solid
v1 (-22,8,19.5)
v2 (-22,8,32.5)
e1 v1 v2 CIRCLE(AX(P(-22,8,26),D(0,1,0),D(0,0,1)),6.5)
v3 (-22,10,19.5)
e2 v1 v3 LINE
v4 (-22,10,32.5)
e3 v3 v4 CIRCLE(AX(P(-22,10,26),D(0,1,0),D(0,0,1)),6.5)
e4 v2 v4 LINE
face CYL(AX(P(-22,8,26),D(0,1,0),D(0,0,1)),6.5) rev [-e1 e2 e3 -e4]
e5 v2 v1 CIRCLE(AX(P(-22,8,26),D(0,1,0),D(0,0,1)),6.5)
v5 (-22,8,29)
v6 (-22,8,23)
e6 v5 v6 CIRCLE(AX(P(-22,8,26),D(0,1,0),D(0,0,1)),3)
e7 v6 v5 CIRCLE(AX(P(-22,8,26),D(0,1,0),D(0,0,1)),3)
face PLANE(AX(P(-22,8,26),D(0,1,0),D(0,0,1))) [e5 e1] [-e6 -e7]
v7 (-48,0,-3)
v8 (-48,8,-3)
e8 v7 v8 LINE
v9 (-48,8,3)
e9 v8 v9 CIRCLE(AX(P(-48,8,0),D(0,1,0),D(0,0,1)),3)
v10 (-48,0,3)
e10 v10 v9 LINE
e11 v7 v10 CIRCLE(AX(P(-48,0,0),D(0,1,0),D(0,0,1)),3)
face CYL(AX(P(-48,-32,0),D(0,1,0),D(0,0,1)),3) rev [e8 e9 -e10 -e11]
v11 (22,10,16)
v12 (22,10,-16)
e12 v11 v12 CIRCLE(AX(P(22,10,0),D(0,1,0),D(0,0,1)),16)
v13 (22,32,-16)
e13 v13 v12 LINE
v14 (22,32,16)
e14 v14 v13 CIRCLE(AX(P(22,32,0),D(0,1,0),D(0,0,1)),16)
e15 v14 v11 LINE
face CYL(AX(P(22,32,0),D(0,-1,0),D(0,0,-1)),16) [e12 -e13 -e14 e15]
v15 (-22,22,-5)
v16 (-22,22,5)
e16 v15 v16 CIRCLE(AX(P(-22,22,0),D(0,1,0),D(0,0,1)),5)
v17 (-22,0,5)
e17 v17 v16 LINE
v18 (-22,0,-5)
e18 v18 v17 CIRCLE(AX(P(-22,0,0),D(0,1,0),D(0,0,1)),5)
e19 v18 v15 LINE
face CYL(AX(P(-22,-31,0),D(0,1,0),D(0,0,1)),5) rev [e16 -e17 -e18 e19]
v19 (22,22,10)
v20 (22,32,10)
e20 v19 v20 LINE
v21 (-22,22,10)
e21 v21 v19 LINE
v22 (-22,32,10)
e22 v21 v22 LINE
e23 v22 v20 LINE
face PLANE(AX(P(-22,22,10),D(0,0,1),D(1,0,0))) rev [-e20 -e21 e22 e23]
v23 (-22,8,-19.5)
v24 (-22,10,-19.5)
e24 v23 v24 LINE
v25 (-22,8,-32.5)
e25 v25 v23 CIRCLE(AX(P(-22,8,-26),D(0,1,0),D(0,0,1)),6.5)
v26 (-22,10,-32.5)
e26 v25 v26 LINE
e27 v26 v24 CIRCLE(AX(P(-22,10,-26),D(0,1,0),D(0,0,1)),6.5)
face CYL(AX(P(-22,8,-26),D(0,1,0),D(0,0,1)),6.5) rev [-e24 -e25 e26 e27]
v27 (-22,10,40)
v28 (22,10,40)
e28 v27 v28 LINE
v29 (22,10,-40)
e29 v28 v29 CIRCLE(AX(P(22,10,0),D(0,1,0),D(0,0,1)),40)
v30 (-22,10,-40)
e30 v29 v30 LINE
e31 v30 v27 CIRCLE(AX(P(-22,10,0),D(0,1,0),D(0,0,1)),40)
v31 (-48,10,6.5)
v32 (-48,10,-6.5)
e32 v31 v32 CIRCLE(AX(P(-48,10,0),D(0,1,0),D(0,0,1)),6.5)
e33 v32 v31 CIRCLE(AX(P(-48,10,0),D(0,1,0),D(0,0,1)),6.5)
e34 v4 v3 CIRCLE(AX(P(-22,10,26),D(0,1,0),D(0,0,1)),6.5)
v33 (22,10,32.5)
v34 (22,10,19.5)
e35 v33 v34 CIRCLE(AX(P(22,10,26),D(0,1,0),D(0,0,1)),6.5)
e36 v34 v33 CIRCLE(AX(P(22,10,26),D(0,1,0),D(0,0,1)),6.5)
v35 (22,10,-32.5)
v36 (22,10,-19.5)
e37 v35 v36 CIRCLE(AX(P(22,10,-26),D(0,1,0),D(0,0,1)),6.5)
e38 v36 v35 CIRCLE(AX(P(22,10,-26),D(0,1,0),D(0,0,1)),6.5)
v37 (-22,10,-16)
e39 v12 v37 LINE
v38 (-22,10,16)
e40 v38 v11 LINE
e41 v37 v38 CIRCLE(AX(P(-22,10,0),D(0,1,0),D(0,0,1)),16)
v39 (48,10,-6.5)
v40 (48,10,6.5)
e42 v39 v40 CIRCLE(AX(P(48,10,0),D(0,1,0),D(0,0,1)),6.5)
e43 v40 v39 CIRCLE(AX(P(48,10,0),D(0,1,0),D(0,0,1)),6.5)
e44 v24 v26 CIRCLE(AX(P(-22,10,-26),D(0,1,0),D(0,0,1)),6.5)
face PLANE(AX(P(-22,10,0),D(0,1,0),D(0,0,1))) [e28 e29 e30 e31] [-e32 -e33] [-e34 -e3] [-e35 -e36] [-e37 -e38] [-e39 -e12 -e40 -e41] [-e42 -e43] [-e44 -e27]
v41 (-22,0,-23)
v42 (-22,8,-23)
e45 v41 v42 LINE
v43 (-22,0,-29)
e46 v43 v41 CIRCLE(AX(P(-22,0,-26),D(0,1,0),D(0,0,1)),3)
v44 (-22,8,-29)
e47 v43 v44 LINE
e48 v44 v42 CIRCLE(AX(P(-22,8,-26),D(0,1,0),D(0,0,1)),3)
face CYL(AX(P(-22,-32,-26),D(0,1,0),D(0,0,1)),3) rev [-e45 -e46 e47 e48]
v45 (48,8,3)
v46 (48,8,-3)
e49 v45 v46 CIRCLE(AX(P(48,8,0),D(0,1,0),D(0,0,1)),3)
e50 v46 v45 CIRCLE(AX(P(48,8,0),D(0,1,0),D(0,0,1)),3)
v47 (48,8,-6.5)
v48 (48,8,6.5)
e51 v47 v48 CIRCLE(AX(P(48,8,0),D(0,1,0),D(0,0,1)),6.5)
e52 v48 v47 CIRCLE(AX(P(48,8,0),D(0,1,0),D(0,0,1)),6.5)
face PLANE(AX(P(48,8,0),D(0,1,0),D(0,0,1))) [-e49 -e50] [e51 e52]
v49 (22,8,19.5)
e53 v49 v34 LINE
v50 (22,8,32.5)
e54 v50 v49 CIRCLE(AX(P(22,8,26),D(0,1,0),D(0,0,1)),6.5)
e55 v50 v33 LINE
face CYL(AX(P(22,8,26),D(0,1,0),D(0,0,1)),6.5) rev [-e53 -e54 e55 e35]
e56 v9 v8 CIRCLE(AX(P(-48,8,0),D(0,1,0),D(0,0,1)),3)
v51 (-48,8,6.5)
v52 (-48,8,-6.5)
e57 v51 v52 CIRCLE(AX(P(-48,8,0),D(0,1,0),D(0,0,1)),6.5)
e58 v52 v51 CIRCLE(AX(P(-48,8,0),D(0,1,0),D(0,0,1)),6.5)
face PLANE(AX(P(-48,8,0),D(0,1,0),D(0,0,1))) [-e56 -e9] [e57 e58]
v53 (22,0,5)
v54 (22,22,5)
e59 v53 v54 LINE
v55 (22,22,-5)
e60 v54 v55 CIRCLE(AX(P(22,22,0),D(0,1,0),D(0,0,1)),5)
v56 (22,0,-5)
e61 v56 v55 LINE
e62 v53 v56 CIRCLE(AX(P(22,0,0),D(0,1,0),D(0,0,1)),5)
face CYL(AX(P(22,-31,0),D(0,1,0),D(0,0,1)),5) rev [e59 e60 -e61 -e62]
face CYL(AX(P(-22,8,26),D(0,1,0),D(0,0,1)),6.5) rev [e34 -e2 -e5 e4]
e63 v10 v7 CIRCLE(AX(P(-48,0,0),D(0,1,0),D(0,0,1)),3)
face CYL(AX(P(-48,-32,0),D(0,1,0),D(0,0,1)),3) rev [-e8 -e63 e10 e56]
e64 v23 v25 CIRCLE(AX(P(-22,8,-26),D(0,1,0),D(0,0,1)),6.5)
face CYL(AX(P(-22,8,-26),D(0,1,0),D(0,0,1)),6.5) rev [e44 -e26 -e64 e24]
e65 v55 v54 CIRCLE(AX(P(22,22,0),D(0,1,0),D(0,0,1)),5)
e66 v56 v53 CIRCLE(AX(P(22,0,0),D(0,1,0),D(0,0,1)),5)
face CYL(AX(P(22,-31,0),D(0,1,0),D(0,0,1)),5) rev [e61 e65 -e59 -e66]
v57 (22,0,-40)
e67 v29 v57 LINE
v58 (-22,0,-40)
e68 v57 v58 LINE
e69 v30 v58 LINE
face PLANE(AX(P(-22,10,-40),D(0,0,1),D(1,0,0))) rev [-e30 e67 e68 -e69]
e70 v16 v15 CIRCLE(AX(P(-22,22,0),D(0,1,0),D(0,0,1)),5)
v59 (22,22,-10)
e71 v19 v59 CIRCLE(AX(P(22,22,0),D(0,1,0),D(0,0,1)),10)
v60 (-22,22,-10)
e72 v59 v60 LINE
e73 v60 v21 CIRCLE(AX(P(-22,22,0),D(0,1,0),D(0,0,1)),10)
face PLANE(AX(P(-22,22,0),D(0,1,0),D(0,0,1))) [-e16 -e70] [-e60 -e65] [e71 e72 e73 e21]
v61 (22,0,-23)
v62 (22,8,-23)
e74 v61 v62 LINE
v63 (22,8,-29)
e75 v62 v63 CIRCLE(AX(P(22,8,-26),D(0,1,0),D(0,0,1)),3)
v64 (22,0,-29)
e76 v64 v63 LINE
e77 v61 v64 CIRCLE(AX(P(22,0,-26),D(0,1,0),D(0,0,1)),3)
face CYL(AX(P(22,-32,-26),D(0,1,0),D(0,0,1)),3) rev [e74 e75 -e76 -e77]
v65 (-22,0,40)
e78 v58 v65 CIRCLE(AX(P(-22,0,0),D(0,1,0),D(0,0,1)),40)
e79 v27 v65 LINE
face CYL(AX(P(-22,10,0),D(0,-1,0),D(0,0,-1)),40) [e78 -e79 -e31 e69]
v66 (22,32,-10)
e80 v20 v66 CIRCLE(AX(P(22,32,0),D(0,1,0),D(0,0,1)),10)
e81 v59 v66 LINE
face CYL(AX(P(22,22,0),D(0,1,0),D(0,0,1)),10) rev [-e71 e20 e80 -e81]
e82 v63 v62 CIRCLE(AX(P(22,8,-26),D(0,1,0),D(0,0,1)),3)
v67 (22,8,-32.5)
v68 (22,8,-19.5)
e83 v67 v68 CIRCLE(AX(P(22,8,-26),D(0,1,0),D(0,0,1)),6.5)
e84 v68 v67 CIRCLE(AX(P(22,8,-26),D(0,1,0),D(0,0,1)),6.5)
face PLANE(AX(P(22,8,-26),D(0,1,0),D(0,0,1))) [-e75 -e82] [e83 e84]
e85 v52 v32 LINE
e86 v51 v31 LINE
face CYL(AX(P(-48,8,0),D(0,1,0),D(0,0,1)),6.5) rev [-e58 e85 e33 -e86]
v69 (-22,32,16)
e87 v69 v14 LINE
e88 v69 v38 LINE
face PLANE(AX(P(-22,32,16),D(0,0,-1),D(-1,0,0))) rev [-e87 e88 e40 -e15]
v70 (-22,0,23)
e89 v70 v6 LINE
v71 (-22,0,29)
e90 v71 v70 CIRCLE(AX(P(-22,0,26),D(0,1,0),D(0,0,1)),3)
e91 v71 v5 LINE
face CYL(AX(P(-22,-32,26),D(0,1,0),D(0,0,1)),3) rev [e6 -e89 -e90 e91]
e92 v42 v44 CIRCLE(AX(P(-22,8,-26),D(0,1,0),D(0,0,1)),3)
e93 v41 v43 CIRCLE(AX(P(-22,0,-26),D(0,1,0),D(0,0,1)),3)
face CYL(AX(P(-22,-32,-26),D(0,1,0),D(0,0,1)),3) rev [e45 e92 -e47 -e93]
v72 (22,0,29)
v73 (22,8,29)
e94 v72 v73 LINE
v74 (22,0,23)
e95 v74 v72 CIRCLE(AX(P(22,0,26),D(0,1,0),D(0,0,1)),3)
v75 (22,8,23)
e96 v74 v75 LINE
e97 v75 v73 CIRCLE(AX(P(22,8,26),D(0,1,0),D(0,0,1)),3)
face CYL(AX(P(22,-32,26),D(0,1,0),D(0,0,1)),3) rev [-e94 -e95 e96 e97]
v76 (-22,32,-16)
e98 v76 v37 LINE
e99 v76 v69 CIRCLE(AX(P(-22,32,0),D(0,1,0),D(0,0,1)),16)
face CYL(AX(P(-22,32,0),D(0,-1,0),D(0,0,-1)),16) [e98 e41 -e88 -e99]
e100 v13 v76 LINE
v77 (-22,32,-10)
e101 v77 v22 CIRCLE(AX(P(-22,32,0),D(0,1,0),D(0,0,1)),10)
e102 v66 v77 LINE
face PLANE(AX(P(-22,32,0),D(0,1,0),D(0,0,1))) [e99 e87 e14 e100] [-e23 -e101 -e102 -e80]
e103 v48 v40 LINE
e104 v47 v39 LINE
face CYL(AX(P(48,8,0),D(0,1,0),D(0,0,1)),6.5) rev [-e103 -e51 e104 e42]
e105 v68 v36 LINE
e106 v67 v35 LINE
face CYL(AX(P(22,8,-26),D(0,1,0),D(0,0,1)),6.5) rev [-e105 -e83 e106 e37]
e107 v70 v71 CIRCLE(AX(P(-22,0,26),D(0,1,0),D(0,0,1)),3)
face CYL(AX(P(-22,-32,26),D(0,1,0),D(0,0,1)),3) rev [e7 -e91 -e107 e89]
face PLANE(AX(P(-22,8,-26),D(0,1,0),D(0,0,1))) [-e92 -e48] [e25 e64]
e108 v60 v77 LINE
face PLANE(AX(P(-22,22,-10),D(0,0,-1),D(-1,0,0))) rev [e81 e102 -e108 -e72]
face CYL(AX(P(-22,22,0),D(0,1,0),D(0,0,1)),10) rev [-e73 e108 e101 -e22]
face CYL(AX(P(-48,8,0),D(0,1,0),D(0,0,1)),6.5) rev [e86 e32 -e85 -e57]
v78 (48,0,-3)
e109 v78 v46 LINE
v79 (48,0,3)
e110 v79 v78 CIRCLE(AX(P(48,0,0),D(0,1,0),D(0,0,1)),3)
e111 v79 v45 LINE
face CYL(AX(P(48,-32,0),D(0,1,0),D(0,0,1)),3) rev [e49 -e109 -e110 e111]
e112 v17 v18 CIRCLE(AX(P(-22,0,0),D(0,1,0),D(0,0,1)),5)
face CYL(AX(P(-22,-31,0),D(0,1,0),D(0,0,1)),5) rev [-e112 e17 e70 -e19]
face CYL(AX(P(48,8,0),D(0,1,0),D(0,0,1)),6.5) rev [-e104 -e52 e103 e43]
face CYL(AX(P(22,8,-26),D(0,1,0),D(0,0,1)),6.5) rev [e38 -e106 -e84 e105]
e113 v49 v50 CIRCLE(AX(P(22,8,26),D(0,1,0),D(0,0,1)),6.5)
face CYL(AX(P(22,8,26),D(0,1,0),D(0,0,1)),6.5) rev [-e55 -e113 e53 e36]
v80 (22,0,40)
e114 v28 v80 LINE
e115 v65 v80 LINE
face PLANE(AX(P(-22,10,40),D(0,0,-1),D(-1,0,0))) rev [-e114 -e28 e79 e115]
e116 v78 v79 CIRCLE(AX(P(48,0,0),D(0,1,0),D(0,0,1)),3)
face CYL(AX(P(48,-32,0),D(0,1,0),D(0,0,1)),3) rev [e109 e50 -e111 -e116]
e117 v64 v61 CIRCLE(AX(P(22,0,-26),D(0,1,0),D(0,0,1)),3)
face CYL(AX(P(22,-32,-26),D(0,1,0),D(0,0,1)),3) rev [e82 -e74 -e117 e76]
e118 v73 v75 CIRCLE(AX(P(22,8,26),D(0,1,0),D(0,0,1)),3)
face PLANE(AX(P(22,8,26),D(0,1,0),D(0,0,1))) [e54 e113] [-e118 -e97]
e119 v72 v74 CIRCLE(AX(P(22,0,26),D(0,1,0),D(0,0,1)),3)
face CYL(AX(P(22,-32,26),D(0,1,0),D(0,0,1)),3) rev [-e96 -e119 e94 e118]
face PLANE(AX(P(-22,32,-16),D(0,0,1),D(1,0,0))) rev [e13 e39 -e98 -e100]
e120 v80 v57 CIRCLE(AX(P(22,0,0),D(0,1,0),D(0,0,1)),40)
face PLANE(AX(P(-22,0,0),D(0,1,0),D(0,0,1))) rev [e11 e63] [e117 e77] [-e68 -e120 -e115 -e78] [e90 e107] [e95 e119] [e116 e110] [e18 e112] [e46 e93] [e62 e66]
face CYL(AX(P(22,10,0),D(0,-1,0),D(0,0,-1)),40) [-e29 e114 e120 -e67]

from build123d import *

# Parameters (mm, degrees)
BASE_FLANGE_DEPTH             = 10
SLOT_BOSS_DEPTH               = 22
SLOT_POCKET_DEPTH             = 10
SLOT_THROUGH_CUT_SKETCH_R     = 5
SLOT_THROUGH_CUT_DEPTH        = 53
COUNTERBORES_SKETCH_R         = 6.5
COUNTERBORES_6X_DEPTH_2_DEPTH = 2
MOUNTING_HOLES_SKETCH_R       = 3
MOUNTING_HOLES_6X_DEPTH       = 40


with BuildPart() as part:
    # Base Flange Sketch → Base Flange (new body)
    with BuildSketch(Plane(origin=(0, 0, 0), x_dir=(1, 0, 0), z_dir=(0, 1, 0))):
        with BuildLine():
            Line((-22, -40), (22, -40))
            ThreePointArc((22, -40), (62, 0), (22, 40))
            Line((22, 40), (-22, 40))
            ThreePointArc((-22, 40), (-62, 0), (-22, -40))
        make_face()
    extrude(amount=BASE_FLANGE_DEPTH)

    # Slot Boss Sketch → Slot Boss (add)
    with BuildSketch(Plane(origin=(0, 10, 0), x_dir=(1, 0, 0), z_dir=(0, 1, 0))):
        with BuildLine():
            Line((-22, 16), (22, 16))
            ThreePointArc((22, 16), (38, 0), (22, -16))
            Line((22, -16), (-22, -16))
            ThreePointArc((-22, -16), (-38, 0), (-22, 16))
        make_face()
    extrude(amount=SLOT_BOSS_DEPTH)

    # Slot Pocket Sketch → Slot Pocket (cut)
    with BuildSketch(Plane(origin=(0, 32, 0), x_dir=(1, 0, 0), z_dir=(0, 1, 0))):
        with BuildLine():
            Line((-22, 10), (22, 10))
            ThreePointArc((22, 10), (32, 0), (22, -10))
            Line((22, -10), (-22, -10))
            ThreePointArc((-22, -10), (-32, 0), (-22, 10))
        make_face()
    extrude(amount=-SLOT_POCKET_DEPTH, mode=Mode.SUBTRACT)

    # Slot Through Cut Sketch → Slot Through Cut (cut)
    with BuildSketch(Plane(origin=(0, 22, 0), x_dir=(1, 0, 0), z_dir=(0, 1, 0))):
        with Locations(Location((22, 0, 0), (0, 0, 270))):
            Circle(SLOT_THROUGH_CUT_SKETCH_R)
        with Locations(Location((-22, 0, 0), (0, 0, 270))):
            Circle(SLOT_THROUGH_CUT_SKETCH_R)
    extrude(amount=-SLOT_THROUGH_CUT_DEPTH, mode=Mode.SUBTRACT)

    # Counterbores Sketch → Counterbores 6x Depth 2 (cut)
    with BuildSketch(Plane(origin=(0, 10, 0), x_dir=(1, 0, 0), z_dir=(0, 1, 0))):
        with Locations(Location((48, 0, 0), (0, 0, 270))):
            Circle(COUNTERBORES_SKETCH_R)
        with Locations(Location((22, 26, 0), (0, 0, 270))):
            Circle(COUNTERBORES_SKETCH_R)
        with Locations(Location((-22, 26, 0), (0, 0, 270))):
            Circle(COUNTERBORES_SKETCH_R)
        with Locations(Location((-48, 0, 0), (0, 0, 270))):
            Circle(COUNTERBORES_SKETCH_R)
        with Locations(Location((-22, -26, 0), (0, 0, 270))):
            Circle(COUNTERBORES_SKETCH_R)
        with Locations(Location((22, -26, 0), (0, 0, 270))):
            Circle(COUNTERBORES_SKETCH_R)
    extrude(amount=-COUNTERBORES_6X_DEPTH_2_DEPTH, mode=Mode.SUBTRACT)

    # Mounting Holes Sketch → Mounting Holes 6x (cut)
    with BuildSketch(Plane(origin=(0, 8, 0), x_dir=(1, 0, 0), z_dir=(0, 1, 0))):
        with Locations(Location((48, 0, 0), (0, 0, 270))):
            Circle(MOUNTING_HOLES_SKETCH_R)
        with Locations(Location((22, -26, 0), (0, 0, 270))):
            Circle(MOUNTING_HOLES_SKETCH_R)
        with Locations(Location((-22, -26, 0), (0, 0, 270))):
            Circle(MOUNTING_HOLES_SKETCH_R)
        with Locations(Location((-48, 0, 0), (0, 0, 270))):
            Circle(MOUNTING_HOLES_SKETCH_R)
        with Locations(Location((-22, 26, 0), (0, 0, 270))):
            Circle(MOUNTING_HOLES_SKETCH_R)
        with Locations(Location((22, 26, 0), (0, 0, 270))):
            Circle(MOUNTING_HOLES_SKETCH_R)
    extrude(amount=-MOUNTING_HOLES_6X_DEPTH, mode=Mode.SUBTRACT)


solid = part.part
